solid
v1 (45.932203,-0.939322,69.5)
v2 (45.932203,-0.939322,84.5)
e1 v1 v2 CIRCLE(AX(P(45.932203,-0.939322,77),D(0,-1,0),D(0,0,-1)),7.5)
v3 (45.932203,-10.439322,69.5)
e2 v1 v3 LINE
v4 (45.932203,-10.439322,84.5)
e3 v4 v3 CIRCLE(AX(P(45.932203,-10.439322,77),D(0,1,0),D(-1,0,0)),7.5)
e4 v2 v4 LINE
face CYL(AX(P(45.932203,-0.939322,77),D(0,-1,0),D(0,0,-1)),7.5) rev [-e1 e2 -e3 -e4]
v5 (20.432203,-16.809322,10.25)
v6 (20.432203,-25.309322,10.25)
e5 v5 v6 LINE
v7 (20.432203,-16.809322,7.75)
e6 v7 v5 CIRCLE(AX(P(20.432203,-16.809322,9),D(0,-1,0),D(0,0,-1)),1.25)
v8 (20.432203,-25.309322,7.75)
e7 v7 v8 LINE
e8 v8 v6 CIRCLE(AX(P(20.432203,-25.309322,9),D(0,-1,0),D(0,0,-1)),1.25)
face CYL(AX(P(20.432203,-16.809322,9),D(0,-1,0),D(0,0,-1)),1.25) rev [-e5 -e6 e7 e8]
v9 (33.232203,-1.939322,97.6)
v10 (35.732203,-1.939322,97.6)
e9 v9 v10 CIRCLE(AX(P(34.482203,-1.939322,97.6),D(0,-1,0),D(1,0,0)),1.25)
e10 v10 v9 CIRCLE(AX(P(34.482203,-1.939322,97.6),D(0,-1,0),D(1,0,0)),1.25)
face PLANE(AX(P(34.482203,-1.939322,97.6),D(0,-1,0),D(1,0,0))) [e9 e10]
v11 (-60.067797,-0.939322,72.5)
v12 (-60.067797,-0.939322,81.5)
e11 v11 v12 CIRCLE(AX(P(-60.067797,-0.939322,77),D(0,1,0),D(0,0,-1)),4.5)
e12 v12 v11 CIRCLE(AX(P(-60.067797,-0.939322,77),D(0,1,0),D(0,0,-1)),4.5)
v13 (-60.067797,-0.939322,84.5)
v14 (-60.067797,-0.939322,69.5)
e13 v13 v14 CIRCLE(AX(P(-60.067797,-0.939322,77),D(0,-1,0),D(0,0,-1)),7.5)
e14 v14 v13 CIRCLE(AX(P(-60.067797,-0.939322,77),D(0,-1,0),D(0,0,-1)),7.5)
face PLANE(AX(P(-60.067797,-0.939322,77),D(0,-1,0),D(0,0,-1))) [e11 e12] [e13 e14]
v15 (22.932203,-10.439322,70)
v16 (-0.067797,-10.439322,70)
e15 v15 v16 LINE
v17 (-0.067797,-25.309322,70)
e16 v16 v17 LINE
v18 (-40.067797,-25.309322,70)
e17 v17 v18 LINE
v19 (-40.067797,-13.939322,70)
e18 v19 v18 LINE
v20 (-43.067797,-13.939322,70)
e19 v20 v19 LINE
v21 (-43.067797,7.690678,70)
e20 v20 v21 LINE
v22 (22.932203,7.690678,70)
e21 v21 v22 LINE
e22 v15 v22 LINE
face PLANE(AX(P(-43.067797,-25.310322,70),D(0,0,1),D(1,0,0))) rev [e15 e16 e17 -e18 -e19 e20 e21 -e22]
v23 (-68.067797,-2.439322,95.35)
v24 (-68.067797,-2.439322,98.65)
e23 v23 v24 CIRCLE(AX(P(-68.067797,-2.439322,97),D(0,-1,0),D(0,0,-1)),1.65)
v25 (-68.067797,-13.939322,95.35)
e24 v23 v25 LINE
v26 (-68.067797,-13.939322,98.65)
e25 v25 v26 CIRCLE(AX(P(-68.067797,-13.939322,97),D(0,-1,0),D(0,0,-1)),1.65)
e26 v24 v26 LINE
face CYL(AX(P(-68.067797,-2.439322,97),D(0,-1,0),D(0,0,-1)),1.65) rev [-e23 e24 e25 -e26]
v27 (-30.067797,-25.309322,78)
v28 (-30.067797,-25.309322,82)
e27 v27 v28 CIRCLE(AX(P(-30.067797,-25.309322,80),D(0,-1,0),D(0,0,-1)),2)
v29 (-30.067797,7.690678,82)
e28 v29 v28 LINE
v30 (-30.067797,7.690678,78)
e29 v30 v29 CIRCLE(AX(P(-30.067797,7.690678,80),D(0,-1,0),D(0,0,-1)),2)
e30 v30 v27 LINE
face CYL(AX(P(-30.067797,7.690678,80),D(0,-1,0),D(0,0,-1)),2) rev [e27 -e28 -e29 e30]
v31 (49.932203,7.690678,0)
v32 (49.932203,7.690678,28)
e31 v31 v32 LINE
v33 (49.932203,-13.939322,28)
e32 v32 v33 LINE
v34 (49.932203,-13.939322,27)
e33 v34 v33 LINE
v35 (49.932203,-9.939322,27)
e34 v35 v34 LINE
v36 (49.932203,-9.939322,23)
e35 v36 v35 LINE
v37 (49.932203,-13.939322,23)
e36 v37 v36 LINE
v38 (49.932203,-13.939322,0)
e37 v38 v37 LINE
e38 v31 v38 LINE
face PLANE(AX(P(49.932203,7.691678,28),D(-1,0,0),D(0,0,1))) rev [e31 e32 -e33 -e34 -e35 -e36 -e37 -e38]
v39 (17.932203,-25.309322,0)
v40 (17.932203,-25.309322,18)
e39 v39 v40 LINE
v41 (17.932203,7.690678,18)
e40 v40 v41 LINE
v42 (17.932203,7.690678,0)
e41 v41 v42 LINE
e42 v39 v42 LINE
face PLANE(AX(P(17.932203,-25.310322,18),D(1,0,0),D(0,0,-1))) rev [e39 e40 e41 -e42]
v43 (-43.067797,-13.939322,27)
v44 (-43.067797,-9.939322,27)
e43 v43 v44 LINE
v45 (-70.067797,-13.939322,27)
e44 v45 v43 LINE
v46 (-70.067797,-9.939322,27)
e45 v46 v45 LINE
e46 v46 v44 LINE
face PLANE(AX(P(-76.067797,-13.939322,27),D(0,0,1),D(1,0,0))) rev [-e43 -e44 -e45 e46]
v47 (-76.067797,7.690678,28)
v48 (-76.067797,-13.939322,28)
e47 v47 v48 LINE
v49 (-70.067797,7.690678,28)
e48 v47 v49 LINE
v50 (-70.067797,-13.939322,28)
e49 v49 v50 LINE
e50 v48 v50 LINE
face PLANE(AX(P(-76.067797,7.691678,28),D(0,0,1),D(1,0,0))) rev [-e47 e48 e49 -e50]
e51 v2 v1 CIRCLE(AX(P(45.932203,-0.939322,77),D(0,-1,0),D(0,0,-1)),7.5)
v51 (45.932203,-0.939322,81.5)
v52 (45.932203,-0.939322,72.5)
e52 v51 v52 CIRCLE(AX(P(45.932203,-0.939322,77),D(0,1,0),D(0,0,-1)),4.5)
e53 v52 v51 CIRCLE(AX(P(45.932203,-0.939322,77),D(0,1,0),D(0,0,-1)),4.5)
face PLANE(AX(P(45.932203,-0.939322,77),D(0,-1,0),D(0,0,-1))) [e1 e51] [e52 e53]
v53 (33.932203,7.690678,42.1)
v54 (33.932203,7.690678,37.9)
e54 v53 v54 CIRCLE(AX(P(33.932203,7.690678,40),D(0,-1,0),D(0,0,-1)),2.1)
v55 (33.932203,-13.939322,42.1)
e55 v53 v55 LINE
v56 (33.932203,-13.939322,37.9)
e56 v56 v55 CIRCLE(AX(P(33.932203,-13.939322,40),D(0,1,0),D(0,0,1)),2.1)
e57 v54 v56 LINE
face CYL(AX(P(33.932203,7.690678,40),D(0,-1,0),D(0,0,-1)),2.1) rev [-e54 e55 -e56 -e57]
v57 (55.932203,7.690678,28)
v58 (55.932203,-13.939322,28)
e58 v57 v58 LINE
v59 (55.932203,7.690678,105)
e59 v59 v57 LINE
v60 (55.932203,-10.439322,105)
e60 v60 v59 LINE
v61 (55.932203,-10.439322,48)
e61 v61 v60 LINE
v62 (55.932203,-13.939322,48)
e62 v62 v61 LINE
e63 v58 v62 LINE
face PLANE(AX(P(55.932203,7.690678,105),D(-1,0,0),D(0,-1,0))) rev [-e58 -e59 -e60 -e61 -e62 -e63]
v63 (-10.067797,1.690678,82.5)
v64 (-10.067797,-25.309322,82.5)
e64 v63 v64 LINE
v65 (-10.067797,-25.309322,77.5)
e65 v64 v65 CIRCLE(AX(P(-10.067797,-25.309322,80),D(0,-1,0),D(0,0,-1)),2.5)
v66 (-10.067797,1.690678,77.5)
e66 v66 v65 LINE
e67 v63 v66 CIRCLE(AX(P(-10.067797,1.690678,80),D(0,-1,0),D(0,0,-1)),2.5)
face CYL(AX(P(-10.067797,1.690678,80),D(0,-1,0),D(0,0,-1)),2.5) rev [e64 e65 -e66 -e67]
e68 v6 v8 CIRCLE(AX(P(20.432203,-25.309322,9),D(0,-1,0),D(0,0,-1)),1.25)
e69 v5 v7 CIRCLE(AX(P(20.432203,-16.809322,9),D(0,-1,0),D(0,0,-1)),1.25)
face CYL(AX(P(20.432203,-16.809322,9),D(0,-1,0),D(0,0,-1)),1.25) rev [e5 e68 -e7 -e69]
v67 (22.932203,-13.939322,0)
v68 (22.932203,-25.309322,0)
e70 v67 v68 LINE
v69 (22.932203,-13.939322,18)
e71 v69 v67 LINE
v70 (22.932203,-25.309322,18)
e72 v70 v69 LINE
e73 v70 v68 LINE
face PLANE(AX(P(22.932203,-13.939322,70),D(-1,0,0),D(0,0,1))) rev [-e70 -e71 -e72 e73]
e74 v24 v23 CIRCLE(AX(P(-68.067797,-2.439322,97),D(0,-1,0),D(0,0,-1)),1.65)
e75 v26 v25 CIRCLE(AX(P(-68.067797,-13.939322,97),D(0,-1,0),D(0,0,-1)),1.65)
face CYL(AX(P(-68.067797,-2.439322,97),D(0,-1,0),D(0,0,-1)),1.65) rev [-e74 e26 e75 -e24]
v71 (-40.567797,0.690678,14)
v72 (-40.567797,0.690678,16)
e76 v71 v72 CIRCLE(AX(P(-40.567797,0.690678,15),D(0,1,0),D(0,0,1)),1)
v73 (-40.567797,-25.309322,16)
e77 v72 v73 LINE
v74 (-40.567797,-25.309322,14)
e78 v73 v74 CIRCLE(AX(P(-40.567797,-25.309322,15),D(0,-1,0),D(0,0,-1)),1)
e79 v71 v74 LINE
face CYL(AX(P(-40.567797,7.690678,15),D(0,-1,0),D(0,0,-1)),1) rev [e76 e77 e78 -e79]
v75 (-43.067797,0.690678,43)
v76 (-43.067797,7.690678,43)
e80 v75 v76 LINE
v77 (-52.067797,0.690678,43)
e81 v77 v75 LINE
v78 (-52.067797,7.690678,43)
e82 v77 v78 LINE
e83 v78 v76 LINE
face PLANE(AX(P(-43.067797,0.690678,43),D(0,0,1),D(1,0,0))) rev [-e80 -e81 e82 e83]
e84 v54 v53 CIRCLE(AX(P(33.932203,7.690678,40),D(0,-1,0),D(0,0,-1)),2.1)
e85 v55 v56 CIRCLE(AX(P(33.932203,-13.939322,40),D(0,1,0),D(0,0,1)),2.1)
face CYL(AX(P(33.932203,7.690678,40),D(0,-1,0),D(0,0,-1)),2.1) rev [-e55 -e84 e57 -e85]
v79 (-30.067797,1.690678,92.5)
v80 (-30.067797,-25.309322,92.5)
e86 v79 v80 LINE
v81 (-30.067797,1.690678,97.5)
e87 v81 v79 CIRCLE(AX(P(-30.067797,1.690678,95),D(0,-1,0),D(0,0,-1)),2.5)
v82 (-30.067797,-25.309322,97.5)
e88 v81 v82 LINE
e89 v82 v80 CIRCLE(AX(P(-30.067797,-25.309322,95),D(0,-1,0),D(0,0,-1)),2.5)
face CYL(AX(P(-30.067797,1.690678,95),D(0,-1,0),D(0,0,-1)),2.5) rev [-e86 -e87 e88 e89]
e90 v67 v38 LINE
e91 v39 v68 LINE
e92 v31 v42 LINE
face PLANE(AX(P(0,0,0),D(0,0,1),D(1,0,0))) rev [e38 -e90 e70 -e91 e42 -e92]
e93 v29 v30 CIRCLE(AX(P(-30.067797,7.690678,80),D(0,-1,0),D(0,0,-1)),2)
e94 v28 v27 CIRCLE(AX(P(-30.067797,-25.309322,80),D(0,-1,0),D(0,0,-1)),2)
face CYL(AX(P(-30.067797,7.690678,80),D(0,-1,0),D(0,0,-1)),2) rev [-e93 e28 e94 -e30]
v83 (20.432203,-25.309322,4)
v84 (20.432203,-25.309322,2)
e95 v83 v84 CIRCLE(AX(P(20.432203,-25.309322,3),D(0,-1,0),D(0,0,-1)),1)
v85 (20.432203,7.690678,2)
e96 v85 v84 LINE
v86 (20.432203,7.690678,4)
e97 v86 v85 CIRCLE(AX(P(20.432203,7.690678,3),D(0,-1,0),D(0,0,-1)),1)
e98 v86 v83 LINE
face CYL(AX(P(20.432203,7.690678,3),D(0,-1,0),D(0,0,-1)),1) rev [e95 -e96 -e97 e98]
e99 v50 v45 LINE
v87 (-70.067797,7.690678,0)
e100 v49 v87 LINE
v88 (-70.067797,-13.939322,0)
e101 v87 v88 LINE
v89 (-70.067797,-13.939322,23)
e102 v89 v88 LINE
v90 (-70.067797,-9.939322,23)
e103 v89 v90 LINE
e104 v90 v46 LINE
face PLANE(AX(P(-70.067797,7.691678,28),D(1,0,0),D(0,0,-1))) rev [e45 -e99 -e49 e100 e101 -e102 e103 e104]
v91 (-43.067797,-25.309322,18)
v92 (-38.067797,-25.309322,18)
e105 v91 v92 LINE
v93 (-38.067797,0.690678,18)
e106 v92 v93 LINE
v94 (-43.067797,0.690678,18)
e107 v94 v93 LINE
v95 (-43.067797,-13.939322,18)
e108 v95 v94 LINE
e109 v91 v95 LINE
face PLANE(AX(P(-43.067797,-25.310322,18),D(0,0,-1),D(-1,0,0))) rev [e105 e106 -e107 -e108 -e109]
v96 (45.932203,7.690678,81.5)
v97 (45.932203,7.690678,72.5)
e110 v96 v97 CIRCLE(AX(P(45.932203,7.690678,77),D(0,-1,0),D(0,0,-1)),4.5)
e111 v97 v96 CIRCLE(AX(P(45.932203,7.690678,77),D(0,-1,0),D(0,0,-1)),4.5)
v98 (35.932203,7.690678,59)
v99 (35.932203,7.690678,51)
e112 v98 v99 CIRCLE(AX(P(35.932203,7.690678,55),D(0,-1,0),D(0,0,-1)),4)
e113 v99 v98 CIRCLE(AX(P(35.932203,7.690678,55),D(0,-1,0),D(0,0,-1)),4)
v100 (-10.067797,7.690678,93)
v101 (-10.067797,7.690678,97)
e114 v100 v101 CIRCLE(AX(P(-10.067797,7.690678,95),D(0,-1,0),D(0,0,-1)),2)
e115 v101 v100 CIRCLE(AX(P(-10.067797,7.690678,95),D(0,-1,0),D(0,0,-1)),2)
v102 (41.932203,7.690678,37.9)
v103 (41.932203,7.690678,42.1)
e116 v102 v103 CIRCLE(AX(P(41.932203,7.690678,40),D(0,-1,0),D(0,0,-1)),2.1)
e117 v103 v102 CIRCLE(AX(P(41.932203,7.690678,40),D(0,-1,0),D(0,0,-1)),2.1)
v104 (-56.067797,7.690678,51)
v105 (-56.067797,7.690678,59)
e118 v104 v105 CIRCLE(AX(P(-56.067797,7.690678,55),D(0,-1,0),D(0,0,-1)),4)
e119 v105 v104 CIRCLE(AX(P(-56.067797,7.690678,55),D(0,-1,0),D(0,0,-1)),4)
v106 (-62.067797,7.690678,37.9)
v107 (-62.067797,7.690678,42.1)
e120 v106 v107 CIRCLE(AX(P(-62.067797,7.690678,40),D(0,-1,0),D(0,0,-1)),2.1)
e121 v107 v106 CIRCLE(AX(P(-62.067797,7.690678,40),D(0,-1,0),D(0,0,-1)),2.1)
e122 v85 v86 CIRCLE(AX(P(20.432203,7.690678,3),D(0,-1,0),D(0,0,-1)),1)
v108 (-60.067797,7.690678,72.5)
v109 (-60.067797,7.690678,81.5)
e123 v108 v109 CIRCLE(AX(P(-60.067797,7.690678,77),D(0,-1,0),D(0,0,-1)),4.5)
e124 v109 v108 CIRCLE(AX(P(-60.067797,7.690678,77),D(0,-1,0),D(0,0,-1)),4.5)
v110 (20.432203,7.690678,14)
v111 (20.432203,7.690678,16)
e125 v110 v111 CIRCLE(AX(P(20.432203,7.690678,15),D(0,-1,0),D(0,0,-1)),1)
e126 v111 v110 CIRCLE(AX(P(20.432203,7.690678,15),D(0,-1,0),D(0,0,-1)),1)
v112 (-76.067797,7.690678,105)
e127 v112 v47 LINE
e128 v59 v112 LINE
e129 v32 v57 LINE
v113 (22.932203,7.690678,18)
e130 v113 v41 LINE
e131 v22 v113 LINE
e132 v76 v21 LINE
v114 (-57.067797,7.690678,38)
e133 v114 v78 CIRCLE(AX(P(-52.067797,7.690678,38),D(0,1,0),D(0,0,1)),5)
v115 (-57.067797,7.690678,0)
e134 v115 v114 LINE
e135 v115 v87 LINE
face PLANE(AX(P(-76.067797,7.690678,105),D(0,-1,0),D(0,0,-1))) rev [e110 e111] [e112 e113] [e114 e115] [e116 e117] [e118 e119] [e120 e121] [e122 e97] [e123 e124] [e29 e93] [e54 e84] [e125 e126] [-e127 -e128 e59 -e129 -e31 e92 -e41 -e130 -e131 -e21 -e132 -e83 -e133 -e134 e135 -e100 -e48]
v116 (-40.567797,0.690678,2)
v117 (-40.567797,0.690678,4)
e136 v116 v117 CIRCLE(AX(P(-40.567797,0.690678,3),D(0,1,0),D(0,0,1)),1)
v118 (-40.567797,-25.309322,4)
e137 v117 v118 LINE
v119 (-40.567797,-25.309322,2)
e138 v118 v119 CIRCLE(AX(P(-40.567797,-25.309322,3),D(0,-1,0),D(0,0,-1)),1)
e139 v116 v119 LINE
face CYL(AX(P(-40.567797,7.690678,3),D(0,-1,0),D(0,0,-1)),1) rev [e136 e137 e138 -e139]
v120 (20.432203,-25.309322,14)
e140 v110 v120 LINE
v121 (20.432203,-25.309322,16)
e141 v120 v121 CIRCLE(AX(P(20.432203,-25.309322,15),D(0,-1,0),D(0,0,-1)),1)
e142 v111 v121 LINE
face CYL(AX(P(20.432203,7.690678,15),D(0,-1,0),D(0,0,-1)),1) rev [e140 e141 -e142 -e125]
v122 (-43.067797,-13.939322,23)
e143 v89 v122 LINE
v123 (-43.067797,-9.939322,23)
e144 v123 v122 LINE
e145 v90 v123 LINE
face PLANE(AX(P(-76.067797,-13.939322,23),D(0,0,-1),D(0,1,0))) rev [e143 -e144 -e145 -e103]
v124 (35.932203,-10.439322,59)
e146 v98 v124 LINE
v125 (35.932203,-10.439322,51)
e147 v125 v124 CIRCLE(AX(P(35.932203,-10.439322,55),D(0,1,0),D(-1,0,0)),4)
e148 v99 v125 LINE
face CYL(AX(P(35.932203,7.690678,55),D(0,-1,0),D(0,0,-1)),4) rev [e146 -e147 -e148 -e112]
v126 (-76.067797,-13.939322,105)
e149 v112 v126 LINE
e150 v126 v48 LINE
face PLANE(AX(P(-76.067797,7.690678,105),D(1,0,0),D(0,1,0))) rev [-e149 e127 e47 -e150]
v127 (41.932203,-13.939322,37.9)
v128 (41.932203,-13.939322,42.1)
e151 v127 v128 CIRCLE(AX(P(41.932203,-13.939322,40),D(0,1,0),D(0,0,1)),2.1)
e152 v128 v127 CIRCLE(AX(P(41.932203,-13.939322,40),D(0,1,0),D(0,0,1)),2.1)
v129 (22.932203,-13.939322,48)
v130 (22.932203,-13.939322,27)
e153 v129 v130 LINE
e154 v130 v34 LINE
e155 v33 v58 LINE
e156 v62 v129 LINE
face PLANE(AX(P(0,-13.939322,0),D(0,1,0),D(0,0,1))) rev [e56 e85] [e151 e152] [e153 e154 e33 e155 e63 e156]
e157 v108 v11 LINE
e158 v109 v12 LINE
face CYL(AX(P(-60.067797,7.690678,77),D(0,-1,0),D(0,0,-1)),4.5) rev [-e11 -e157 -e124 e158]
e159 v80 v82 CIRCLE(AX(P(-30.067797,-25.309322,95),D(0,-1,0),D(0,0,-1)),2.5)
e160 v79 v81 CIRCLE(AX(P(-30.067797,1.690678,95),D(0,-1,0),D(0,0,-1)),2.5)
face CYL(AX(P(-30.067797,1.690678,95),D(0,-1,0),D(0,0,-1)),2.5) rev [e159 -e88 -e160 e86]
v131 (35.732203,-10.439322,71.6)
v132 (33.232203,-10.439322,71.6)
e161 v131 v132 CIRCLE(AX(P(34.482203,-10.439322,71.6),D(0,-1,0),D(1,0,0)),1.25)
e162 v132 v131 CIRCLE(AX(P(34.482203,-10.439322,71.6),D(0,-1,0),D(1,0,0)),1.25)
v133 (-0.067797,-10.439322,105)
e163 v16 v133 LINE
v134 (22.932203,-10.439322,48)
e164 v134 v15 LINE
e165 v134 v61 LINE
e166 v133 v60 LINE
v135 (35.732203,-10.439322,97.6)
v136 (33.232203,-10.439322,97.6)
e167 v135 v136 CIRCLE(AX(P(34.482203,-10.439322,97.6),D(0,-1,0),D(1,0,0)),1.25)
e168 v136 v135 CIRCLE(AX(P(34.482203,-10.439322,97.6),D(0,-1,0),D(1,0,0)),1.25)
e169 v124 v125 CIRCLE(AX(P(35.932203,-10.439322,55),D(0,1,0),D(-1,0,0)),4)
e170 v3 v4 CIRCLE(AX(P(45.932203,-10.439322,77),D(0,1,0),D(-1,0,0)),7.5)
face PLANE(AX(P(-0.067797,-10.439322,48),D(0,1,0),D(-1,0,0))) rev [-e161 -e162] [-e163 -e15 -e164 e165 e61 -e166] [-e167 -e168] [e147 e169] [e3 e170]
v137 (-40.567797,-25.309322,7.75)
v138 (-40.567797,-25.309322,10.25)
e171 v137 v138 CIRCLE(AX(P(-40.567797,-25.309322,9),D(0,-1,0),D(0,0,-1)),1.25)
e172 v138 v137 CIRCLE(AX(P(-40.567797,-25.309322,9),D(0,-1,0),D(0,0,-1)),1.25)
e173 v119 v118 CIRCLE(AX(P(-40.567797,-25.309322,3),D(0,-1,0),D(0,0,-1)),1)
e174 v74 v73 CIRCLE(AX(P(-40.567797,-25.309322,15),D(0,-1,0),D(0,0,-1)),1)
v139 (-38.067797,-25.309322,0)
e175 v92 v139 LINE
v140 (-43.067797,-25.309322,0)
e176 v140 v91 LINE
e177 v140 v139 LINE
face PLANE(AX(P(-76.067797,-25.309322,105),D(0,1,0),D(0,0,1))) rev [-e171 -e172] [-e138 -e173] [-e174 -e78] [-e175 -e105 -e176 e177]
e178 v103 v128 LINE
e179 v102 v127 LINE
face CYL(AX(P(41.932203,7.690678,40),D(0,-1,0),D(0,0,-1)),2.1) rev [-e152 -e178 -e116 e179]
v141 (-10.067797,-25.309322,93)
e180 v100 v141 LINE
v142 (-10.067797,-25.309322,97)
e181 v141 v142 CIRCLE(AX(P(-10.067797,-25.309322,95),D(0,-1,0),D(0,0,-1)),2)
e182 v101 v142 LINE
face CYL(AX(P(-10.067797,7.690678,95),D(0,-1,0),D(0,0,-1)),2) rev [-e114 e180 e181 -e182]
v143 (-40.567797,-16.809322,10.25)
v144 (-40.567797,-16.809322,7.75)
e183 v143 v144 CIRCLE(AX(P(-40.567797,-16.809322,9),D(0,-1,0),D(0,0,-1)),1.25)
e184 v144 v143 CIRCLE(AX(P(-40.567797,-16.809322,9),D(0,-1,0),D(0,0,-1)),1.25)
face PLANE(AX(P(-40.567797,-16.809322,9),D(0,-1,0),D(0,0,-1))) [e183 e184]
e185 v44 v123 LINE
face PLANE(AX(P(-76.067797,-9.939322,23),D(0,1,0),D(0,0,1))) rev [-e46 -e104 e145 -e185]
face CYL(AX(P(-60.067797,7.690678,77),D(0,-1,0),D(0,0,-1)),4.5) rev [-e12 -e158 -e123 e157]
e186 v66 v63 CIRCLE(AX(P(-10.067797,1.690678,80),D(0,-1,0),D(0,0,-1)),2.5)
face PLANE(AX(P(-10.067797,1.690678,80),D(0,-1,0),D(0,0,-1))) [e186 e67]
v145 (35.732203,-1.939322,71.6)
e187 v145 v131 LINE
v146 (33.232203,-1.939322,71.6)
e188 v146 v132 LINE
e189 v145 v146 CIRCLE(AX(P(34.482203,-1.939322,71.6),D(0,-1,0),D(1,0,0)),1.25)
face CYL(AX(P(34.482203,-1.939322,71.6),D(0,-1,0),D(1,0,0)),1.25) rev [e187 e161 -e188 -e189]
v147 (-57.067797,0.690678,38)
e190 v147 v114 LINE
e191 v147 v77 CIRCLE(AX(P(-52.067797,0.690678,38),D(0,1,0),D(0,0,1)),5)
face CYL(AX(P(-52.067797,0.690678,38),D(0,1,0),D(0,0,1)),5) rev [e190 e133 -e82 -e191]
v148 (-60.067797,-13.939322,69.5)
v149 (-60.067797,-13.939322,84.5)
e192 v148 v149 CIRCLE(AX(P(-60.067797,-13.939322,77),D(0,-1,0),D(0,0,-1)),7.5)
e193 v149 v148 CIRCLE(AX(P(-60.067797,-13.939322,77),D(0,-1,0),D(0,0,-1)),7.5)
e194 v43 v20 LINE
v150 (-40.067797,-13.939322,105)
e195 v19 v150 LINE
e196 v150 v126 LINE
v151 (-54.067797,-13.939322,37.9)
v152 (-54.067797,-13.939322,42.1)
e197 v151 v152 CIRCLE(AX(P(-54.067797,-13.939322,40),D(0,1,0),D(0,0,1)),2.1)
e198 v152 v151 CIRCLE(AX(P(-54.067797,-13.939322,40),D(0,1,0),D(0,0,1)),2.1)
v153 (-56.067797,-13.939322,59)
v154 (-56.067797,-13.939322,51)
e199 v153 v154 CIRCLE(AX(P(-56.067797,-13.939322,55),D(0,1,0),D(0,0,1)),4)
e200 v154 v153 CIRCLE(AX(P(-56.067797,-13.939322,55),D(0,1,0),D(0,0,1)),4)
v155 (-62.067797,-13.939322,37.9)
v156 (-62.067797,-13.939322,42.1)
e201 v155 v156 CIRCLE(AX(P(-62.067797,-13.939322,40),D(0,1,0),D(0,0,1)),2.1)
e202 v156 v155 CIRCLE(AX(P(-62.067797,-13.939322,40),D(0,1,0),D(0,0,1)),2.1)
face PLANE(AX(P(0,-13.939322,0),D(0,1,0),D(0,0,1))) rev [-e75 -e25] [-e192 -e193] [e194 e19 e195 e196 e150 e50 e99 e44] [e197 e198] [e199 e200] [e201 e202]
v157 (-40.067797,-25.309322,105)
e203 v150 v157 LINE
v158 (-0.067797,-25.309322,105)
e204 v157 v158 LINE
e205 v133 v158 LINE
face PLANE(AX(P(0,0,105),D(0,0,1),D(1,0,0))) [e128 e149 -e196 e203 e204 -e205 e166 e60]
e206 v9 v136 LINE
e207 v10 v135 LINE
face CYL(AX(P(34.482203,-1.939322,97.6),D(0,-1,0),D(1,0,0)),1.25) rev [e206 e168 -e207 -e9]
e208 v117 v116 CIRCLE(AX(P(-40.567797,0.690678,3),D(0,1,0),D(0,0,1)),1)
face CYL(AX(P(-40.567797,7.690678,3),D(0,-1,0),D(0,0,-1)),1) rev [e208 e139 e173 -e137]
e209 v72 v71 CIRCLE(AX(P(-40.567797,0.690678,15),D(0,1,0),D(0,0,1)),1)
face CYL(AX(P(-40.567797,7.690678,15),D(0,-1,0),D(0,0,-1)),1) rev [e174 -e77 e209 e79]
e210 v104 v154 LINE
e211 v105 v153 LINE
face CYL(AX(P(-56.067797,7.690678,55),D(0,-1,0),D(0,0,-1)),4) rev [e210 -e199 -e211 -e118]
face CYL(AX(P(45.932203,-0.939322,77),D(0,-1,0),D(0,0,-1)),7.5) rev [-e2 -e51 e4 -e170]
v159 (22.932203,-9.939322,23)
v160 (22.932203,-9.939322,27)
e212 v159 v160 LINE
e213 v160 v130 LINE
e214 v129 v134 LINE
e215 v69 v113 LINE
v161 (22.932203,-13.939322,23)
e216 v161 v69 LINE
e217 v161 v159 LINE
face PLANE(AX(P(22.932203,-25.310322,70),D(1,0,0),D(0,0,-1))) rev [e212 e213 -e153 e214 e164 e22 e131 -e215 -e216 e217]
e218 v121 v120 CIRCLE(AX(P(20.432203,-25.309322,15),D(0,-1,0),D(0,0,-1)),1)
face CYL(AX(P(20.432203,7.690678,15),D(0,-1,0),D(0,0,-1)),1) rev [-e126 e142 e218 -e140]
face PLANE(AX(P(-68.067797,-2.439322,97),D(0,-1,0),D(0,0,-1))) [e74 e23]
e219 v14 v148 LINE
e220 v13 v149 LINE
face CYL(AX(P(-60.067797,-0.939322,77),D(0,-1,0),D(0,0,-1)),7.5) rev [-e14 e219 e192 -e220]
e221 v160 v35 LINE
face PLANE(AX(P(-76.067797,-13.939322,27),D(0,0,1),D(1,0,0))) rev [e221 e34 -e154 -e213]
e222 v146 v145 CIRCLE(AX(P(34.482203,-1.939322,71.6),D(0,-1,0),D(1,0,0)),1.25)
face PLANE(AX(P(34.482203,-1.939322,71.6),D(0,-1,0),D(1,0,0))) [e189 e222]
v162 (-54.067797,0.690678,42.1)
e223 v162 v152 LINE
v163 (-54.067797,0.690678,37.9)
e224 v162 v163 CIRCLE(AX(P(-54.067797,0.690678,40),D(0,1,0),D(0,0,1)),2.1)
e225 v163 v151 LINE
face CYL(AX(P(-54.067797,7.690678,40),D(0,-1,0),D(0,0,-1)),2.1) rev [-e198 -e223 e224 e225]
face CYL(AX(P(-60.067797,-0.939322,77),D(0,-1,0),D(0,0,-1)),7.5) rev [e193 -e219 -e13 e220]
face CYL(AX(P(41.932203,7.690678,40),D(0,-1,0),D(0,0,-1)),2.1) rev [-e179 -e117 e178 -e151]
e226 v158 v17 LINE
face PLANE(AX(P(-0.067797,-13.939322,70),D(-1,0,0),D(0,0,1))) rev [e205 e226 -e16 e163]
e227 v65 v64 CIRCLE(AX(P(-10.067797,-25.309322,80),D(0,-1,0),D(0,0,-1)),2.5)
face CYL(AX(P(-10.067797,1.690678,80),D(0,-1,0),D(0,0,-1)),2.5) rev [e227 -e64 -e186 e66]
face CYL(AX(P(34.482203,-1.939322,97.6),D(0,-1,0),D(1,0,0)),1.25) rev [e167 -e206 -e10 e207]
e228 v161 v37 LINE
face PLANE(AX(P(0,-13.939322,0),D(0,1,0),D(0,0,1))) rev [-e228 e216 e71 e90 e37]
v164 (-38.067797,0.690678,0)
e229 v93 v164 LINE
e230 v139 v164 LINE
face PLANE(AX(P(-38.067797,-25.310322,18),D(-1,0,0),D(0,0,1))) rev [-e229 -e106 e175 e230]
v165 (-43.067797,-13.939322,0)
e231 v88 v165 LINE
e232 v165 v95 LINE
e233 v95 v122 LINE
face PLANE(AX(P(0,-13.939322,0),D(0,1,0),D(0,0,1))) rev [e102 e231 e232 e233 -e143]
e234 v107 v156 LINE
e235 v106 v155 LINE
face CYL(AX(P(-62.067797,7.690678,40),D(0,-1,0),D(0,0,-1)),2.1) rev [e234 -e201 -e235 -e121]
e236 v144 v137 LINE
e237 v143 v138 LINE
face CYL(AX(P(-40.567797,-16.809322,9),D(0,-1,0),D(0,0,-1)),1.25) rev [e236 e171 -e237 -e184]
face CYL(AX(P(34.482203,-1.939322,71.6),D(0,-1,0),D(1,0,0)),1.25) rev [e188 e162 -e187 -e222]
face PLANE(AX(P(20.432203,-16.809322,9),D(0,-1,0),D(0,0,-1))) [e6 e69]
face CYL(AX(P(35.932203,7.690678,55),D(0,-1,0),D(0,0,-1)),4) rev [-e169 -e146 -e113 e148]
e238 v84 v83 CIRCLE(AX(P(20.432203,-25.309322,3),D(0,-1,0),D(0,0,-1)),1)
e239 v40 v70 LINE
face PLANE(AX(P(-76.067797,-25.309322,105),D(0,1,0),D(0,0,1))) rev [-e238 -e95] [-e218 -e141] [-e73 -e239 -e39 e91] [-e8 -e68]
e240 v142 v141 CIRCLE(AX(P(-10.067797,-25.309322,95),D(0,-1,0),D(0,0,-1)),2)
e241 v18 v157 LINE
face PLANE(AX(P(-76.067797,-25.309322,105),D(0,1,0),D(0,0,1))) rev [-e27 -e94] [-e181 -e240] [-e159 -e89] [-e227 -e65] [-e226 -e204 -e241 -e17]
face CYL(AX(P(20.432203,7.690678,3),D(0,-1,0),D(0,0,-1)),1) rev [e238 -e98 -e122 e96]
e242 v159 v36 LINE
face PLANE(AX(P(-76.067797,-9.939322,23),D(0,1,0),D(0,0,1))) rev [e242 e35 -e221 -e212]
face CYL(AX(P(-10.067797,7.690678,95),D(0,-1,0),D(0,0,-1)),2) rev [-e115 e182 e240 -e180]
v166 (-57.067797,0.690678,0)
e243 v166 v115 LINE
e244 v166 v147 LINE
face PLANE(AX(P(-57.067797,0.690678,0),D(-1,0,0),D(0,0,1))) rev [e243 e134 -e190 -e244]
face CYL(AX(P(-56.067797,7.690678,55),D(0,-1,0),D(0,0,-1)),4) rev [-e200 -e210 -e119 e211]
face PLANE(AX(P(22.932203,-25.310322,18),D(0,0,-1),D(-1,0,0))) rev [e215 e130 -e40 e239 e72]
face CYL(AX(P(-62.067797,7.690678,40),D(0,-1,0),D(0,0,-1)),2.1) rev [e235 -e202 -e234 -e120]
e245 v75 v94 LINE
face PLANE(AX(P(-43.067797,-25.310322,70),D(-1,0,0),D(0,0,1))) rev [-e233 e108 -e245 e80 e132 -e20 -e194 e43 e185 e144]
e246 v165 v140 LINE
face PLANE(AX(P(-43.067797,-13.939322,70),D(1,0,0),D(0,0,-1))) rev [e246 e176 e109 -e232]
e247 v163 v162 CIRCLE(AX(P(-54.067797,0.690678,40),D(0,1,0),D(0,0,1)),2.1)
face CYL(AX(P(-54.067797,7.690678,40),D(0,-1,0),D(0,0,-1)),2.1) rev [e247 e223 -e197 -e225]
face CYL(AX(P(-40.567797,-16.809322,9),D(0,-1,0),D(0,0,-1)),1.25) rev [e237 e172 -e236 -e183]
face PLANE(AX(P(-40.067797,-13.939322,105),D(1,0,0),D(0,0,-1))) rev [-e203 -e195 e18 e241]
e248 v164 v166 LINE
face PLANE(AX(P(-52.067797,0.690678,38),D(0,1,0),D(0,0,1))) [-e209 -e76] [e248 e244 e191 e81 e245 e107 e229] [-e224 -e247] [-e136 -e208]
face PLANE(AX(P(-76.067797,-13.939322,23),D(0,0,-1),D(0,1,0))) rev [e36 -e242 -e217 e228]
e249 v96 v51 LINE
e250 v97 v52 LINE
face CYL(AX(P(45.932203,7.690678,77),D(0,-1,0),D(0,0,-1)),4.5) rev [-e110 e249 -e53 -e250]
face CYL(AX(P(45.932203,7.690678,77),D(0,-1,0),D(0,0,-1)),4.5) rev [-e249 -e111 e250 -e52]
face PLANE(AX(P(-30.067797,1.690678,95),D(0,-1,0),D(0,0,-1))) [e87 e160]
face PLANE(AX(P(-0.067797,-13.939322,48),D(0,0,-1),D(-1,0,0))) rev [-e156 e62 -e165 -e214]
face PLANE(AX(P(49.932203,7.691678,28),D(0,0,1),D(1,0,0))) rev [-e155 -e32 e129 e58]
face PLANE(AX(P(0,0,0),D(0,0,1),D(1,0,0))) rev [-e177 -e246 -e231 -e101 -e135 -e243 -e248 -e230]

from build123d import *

# Parameters (mm, degrees)
SKETCH_1_W           = 132
SKETCH_1_H           = 33
EXTRUDE_1_DEPTH      = 105
CUT_EXTRUDE_1_REACH  = 135.792
CUT_EXTRUDE_2_DEPTH  = 11.37
CUT_EXTRUDE_3_REACH  = 135.792
SKETCH_4_W           = 6
SKETCH_4_H           = 28
SKETCH_5_W           = 57
SKETCH_5_H           = 3.5
CUT_EXTRUDE_5_DEPTH  = 56
SKETCH_7_W           = 4
SKETCH_7_H           = 4
CUT_EXTRUDE_6_DEPTH  = 166.956505693
CUT_EXTRUDE_7_DEPTH  = 7
SKETCH_9_R           = 2
SKETCH_9_R_2         = 4.5
SKETCH_9_R_3         = 4
SKETCH_9_R_4         = 2.1
SKETCH_9_R_5         = 1
CUT_EXTRUDE_8_DEPTH  = 134.79203893
SKETCH_10_R          = 7.5
CUT_EXTRUDE_9_DEPTH  = 13
SKETCH_11_R          = 2.5
CUT_EXTRUDE_10_DEPTH = 27
SKETCH_12_R          = 1.25
CUT_EXTRUDE_11_DEPTH = 8.5
SKETCH_13_R          = 1.65
CUT_EXTRUDE_12_DEPTH = 11.5
SKETCH_16_R          = 1.25
CUT_EXTRUDE_13_DEPTH = 8.5


with BuildPart() as part:
    # 草图1 → 凸台-拉伸1 (new body)
    with BuildSketch(Plane.XY):
        with Locations((-10.06779661, -8.809322034)):
            Rectangle(SKETCH_1_W, SKETCH_1_H)
    extrude(amount=EXTRUDE_1_DEPTH)

    # 草图2 → 切除-拉伸1 (cut, up to next)
    with BuildSketch(Plane(origin=(0, 7.690677966, 0), x_dir=(1, 0, 0), z_dir=(0, 1, 0)), mode=Mode.PRIVATE) as cut_extrude_1_sk1:
        Polygon((-43.06779661, -70), (22.93220339, -70), (22.93220339, -18), (17.93220339, -18), (17.93220339, 0), (-38.06779661, 0), (-38.06779661, -18), (-43.06779661, -18), align=None)
    cut_extrude_1_tool1 = extrude(cut_extrude_1_sk1.sketch, amount=-CUT_EXTRUDE_1_REACH, mode=Mode.PRIVATE) & part.part
    add(cut_extrude_1_tool1.solids().sort_by_distance((-10.067797, 7.690678, 36.054054))[0], mode=Mode.SUBTRACT)

    # 草图3 → 切除-拉伸2 (cut)
    with BuildSketch(Plane.XZ.offset(25.309322034)):
        Polygon((-0.06779661, 70), (-0.06779661, 105), (55.93220339, 105), (55.93220339, 28), (49.93220339, 28), (49.93220339, 0), (22.93220339, 0), (22.93220339, 70), align=None)
        Polygon((-40.06779661, 105), (-40.06779661, 70), (-43.06779661, 70), (-43.06779661, 0), (-70.06779661, 0), (-70.06779661, 28), (-76.06779661, 28), (-76.06779661, 105), align=None)
    extrude(amount=-CUT_EXTRUDE_2_DEPTH, mode=Mode.SUBTRACT)

    # 草图4 → 切除-拉伸3 (cut, up to next)
    with BuildSketch(Plane.XZ.offset(25.309322034), mode=Mode.PRIVATE) as cut_extrude_3_sk1:
        with Locations((-73.06779661, 14)):
            Rectangle(SKETCH_4_W, SKETCH_4_H)
    cut_extrude_3_tool1 = extrude(cut_extrude_3_sk1.sketch, amount=-CUT_EXTRUDE_3_REACH, mode=Mode.PRIVATE) & part.part
    # 草图4 → 切除-拉伸3 (cut, up to next)
    with BuildSketch(Plane.XZ.offset(25.309322034), mode=Mode.PRIVATE) as cut_extrude_3_sk2:
        with Locations((52.93220339, 14)):
            Rectangle(SKETCH_4_W, SKETCH_4_H)
    cut_extrude_3_tool2 = extrude(cut_extrude_3_sk2.sketch, amount=-CUT_EXTRUDE_3_REACH, mode=Mode.PRIVATE) & part.part
    add(cut_extrude_3_tool1.solids().sort_by_distance((-73.067797, -25.309322, 14))[0], mode=Mode.SUBTRACT)
    add(cut_extrude_3_tool2.solids().sort_by_distance((52.932203, -25.309322, 14))[0], mode=Mode.SUBTRACT)

    # 草图5 → 切除-拉伸5 (cut)
    with BuildSketch(Plane(origin=(55.93220339, 0, 0), x_dir=(0, 0, -1), z_dir=(1, 0, 0))):
        with Locations((-76.5, -12.189322034)):
            Rectangle(SKETCH_5_W, SKETCH_5_H)
    extrude(amount=-CUT_EXTRUDE_5_DEPTH, mode=Mode.SUBTRACT)

    # 草图7 → 切除-拉伸6 (cut, through all)
    with BuildSketch(Plane(origin=(49.93220339, 0, 0), x_dir=(0, 0, -1), z_dir=(1, 0, 0))):
        with Locations((-25, -11.939322034)):
            Rectangle(SKETCH_7_W, SKETCH_7_H)
    extrude(amount=-CUT_EXTRUDE_6_DEPTH, mode=Mode.SUBTRACT)

    # 草图8 → 切除-拉伸7 (cut)
    with BuildSketch(Plane(origin=(0, 7.690677966, 0), x_dir=(1, 0, 0), z_dir=(0, 1, 0))):
        with BuildLine():
            Line((-38.06779661, -18), (-43.06779661, -18))
            Line((-43.06779661, -18), (-43.06779661, -43))
            Line((-43.06779661, -43), (-52.06779661, -43))
            ThreePointArc((-52.06779661, -43), (-55.603330516, -41.535533906), (-57.06779661, -38))
            Line((-57.06779661, -38), (-57.06779661, 0))
            Line((-57.06779661, 0), (-38.06779661, 0))
            Line((-38.06779661, 0), (-38.06779661, -18))
        make_face()
    extrude(amount=-CUT_EXTRUDE_7_DEPTH, mode=Mode.SUBTRACT)

    # 草图9 → 切除-拉伸8 (cut, through all)
    with BuildSketch(Plane.XZ.offset(25.309322034)):
        with Locations(Location((-10.06779661, 95, 0), (0, 0, 270))):
            Circle(SKETCH_9_R)
        with Locations(Location((-30.06779661, 80, 0), (0, 0, 270))):
            Circle(SKETCH_9_R)
        with Locations(Location((-60.06779661, 77, 0), (0, 0, 270))):
            Circle(SKETCH_9_R_2)
        with Locations(Location((-56.06779661, 55, 0), (0, 0, 270))):
            Circle(SKETCH_9_R_3)
        with Locations(Location((-54.06779661, 40, 0), (0, 0, 90))):
            Circle(SKETCH_9_R_4)
        with Locations(Location((-62.06779661, 40, 0), (0, 0, 270))):
            Circle(SKETCH_9_R_4)
        with Locations(Location((-40.56779661, 15, 0), (0, 0, 270))):
            Circle(SKETCH_9_R_5)
        with Locations(Location((-40.56779661, 3, 0), (0, 0, 270))):
            Circle(SKETCH_9_R_5)
        with Locations(Location((45.93220339, 77, 0), (0, 0, 270))):
            Circle(SKETCH_9_R_2)
        with Locations(Location((35.93220339, 55, 0), (0, 0, 270))):
            Circle(SKETCH_9_R_3)
        with Locations(Location((20.43220339, 15, 0), (0, 0, 270))):
            Circle(SKETCH_9_R_5)
        with Locations(Location((20.43220339, 3, 0), (0, 0, 270))):
            Circle(SKETCH_9_R_5)
        with Locations(Location((41.93220339, 40, 0), (0, 0, 270))):
            Circle(SKETCH_9_R_4)
        with Locations(Location((33.93220339, 40, 0), (0, 0, 270))):
            Circle(SKETCH_9_R_4)
    extrude(amount=-CUT_EXTRUDE_8_DEPTH, mode=Mode.SUBTRACT)

    # 草图10 → 切除-拉伸9 (cut)
    with BuildSketch(Plane.XZ.offset(13.939322034)):
        with Locations(Location((-60.06779661, 77, 0), (0, 0, 270))):
            Circle(SKETCH_10_R)
        with Locations(Location((45.93220339, 77, 0), (0, 0, 270))):
            Circle(SKETCH_10_R)
    extrude(amount=-CUT_EXTRUDE_9_DEPTH, mode=Mode.SUBTRACT)

    # 草图11 → 切除-拉伸10 (cut)
    with BuildSketch(Plane.XZ.offset(25.309322034)):
        with Locations(Location((-30.06779661, 95, 0), (0, 0, 270))):
            Circle(SKETCH_11_R)
        with Locations(Location((-10.06779661, 80, 0), (0, 0, 270))):
            Circle(SKETCH_11_R)
    extrude(amount=-CUT_EXTRUDE_10_DEPTH, mode=Mode.SUBTRACT)

    # 草图12 → 切除-拉伸11 (cut)
    with BuildSketch(Plane.XZ.offset(10.439322034)):
        with Locations((34.48220339, 97.6)):
            Circle(SKETCH_12_R)
        with Locations((34.48220339, 71.6)):
            Circle(SKETCH_12_R)
    extrude(amount=-CUT_EXTRUDE_11_DEPTH, mode=Mode.SUBTRACT)

    # 草图13 → 切除-拉伸12 (cut)
    with BuildSketch(Plane.XZ.offset(13.939322034)):
        with Locations(Location((-68.06779661, 97, 0), (0, 0, 270))):
            Circle(SKETCH_13_R)
    extrude(amount=-CUT_EXTRUDE_12_DEPTH, mode=Mode.SUBTRACT)

    # 草图16 → 切除-拉伸13 (cut)
    with BuildSketch(Plane.XZ.offset(25.309322034)):
        with Locations(Location((-40.56779661, 9, 0), (0, 0, 270))):
            Circle(SKETCH_16_R)
        with Locations(Location((20.43220339, 9, 0), (0, 0, 270))):
            Circle(SKETCH_16_R)
    extrude(amount=-CUT_EXTRUDE_13_DEPTH, mode=Mode.SUBTRACT)


solid = part.part
